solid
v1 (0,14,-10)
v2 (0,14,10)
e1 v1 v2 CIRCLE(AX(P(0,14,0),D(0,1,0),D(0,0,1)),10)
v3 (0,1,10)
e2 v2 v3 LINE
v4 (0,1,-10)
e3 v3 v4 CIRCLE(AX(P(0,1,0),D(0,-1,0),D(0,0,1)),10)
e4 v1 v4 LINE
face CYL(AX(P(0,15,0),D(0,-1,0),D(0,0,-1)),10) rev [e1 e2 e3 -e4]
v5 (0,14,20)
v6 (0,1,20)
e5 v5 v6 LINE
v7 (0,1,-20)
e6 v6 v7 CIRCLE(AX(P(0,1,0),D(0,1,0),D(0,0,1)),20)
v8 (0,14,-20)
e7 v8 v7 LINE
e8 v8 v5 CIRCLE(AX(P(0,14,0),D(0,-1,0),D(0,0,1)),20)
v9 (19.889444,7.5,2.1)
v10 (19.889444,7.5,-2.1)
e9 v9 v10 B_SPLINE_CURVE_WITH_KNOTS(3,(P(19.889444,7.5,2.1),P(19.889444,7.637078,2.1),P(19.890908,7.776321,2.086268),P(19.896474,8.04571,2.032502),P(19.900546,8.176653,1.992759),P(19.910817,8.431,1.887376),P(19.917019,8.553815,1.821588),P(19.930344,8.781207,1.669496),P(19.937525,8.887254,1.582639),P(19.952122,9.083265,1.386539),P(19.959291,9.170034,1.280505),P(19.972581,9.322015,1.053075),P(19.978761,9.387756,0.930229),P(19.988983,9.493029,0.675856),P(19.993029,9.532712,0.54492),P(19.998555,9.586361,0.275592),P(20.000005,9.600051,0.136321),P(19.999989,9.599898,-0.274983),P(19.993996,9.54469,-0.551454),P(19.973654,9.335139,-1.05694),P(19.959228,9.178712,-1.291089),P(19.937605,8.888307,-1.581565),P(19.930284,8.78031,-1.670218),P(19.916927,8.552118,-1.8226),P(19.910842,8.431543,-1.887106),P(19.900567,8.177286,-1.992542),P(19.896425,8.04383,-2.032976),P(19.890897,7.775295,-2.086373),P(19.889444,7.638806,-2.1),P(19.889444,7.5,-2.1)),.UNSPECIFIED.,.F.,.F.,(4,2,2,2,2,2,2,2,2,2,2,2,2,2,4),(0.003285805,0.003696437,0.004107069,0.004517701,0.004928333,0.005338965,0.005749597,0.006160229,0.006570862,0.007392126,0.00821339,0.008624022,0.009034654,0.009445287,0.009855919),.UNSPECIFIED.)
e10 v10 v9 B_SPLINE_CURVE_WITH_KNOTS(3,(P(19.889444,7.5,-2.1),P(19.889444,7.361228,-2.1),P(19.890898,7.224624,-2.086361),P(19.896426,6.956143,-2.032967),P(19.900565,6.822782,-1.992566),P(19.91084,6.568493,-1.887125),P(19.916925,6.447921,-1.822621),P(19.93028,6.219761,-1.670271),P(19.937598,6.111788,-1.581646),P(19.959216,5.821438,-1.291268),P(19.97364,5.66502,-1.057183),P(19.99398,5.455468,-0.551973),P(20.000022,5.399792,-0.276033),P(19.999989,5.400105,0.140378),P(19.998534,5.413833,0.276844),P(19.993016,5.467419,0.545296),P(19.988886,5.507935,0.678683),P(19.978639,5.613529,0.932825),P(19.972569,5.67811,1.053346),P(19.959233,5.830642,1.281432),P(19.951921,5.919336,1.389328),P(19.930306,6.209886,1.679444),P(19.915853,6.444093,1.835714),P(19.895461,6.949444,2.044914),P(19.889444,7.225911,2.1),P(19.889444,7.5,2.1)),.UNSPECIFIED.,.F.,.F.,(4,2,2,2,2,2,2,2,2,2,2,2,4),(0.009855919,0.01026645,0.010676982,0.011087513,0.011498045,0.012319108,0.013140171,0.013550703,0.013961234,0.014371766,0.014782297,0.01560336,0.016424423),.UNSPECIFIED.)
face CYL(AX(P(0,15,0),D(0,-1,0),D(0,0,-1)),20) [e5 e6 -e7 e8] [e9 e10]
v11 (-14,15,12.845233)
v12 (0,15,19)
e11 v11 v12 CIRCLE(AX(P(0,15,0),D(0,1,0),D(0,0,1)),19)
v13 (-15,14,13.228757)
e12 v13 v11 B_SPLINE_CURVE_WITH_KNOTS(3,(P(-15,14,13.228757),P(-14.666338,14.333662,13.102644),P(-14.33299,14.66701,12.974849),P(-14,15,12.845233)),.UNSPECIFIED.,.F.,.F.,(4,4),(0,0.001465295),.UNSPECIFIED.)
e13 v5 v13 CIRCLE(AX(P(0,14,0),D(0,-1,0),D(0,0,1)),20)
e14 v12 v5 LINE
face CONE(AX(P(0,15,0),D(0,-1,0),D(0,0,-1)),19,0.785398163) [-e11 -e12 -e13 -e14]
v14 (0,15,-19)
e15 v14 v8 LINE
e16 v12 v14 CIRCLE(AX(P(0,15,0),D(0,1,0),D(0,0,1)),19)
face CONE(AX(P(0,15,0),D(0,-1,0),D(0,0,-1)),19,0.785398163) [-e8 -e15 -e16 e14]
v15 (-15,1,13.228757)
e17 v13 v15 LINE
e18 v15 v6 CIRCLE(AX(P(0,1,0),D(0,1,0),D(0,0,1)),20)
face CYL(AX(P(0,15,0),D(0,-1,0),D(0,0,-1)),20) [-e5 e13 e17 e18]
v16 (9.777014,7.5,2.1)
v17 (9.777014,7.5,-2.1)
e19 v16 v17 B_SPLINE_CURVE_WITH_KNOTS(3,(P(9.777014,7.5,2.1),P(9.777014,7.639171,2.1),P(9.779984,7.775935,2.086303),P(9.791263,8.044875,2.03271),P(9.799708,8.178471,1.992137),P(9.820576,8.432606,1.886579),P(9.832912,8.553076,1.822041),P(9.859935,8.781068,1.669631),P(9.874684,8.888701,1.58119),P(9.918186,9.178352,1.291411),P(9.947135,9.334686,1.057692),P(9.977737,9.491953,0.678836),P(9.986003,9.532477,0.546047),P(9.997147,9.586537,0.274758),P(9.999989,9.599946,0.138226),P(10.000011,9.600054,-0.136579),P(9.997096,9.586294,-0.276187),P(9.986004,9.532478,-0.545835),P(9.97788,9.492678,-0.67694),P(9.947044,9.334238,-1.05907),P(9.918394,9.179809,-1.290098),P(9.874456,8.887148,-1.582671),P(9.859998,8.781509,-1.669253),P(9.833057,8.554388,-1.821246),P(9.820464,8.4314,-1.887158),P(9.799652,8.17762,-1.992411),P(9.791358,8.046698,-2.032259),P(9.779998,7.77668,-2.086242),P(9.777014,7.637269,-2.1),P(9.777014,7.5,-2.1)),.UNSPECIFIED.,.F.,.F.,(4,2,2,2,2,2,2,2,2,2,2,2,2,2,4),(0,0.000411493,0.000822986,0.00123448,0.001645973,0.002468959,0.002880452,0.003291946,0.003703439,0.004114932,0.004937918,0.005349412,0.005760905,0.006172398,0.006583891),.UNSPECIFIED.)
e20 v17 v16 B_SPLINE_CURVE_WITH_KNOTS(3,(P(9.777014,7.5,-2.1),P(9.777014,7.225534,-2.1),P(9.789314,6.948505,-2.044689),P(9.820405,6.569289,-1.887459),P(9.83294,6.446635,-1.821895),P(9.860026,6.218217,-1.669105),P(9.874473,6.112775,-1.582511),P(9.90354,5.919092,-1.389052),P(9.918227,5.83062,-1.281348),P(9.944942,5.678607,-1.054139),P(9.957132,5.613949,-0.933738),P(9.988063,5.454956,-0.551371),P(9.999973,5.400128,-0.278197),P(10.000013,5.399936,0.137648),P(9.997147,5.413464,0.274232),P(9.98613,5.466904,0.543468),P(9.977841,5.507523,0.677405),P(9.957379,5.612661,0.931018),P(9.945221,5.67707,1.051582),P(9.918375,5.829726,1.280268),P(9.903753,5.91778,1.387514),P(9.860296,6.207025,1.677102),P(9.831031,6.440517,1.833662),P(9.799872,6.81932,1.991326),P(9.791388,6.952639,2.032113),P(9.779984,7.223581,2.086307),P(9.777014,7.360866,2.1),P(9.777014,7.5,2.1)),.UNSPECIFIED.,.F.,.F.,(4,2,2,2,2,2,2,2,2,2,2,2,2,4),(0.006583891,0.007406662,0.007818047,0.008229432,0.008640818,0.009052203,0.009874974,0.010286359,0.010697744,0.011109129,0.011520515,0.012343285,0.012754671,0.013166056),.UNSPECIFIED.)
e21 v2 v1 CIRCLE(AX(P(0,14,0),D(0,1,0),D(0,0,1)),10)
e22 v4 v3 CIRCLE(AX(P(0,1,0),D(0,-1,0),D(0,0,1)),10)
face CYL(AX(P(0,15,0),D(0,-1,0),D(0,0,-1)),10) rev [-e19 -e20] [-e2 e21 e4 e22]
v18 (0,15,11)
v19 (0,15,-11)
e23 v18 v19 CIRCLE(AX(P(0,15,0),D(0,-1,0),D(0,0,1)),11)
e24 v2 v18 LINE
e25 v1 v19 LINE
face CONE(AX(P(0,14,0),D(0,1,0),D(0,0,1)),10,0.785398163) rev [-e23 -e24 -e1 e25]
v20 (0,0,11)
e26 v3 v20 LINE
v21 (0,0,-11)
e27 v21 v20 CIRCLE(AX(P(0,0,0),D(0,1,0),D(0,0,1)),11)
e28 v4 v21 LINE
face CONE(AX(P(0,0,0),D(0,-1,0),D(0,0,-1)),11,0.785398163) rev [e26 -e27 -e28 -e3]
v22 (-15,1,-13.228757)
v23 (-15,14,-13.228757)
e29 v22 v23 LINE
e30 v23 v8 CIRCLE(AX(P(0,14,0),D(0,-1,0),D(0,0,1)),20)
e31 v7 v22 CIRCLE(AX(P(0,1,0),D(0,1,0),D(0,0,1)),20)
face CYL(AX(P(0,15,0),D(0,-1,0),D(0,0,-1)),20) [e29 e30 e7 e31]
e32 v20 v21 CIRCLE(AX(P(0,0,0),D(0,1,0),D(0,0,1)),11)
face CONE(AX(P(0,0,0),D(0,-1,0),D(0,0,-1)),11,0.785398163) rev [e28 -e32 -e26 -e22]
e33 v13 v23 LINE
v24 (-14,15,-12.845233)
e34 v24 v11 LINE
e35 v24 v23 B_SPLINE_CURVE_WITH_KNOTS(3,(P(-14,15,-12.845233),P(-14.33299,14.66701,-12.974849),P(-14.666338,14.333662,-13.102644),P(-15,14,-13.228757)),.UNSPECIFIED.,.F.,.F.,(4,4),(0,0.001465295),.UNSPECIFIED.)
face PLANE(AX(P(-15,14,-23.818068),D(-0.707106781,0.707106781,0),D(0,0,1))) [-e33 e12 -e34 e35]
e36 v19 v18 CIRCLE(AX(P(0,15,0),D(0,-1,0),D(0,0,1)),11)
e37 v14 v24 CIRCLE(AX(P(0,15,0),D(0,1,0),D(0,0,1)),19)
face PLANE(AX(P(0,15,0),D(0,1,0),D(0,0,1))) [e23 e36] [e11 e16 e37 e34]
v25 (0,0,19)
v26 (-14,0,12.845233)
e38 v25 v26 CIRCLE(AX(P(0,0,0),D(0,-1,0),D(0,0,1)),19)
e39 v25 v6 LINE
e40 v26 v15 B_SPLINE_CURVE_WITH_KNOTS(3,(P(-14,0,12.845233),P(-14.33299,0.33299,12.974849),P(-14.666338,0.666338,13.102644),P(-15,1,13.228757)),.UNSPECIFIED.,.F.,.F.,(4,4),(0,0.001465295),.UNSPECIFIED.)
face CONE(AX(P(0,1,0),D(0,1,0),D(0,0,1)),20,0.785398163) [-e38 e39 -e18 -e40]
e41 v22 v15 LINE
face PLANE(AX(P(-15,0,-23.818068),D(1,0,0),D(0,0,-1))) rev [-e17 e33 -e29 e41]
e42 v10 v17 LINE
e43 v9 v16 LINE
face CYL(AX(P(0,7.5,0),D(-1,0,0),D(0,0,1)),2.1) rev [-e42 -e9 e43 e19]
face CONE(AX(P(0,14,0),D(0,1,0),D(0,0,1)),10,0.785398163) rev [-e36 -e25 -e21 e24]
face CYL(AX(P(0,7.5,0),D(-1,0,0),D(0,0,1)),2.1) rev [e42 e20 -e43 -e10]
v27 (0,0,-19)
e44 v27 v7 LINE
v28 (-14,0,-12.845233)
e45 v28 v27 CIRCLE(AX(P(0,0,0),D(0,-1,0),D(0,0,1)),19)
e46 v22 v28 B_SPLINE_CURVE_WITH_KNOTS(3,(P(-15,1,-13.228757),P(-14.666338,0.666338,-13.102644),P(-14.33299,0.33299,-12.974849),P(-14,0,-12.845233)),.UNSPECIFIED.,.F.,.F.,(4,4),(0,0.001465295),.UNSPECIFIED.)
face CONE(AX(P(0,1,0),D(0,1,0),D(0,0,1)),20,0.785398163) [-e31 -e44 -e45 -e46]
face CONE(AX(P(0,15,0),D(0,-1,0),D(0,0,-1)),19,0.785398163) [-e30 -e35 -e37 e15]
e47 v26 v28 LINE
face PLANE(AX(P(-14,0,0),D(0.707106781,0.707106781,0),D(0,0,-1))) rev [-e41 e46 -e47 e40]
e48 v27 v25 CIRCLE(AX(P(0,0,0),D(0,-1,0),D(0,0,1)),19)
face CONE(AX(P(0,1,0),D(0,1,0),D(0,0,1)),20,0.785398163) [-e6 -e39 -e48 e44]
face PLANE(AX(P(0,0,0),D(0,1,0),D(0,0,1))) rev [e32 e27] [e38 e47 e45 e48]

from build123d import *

# Parameters (mm, degrees)
SKETCH_1_R          = 20
SKETCH_1_R_2        = 10
EXTRUDE_1_DEPTH     = 15
SKETCH_2_W          = 9.046336772
SKETCH_2_H          = 38.953764593
CUT_EXTRUDE_1_DEPTH = 33.015621187
CHAMFER_1_SIZE      = 1
SKETCH_3_W          = 2.1
SKETCH_3_H          = 20


with BuildPart() as part:
    # 草图1 → 凸台-拉伸1 (new body)
    with BuildSketch(Plane(origin=(0, 0, 0), x_dir=(1, 0, 0), z_dir=(0, 1, 0))):
        with Locations(Location((0, 0, 0), (0, 0, 270))):
            Circle(SKETCH_1_R)
        with Locations(Location((0, 0, 0), (0, 0, 270))):
            Circle(SKETCH_1_R_2, mode=Mode.SUBTRACT)
    extrude(amount=EXTRUDE_1_DEPTH)

    # 草图2 → 切除-拉伸1 (cut, through all)
    with BuildSketch(Plane(origin=(0, 15, 0), x_dir=(1, 0, 0), z_dir=(0, 1, 0))):
        with Locations((-19.523168386, 4.341186033)):
            Rectangle(SKETCH_2_W, SKETCH_2_H)
    extrude(amount=-CUT_EXTRUDE_1_DEPTH, mode=Mode.SUBTRACT)

    # 倒角1
    chamfer_1_edges = [part.edges().sort_by_distance(p)[0] for p in [
        (20, 15, 0),
        (20, 0, 0),
        (-15, 0, 0),
        (-15, 15, 0),
        (0, 0, -10),
        (0, 15, -10),
    ]]
    chamfer(chamfer_1_edges, length=CHAMFER_1_SIZE)

    # 草图3 → M5 螺纹孔1 (revolve, cut)
    with BuildSketch(Plane.ZX.offset(7.5)):
        with Locations((1.05, 10)):
            Rectangle(SKETCH_3_W, SKETCH_3_H)
    revolve(axis=Axis((-6.35, 7.5, 0), (1, 0, 0)), mode=Mode.SUBTRACT)


solid = part.part
